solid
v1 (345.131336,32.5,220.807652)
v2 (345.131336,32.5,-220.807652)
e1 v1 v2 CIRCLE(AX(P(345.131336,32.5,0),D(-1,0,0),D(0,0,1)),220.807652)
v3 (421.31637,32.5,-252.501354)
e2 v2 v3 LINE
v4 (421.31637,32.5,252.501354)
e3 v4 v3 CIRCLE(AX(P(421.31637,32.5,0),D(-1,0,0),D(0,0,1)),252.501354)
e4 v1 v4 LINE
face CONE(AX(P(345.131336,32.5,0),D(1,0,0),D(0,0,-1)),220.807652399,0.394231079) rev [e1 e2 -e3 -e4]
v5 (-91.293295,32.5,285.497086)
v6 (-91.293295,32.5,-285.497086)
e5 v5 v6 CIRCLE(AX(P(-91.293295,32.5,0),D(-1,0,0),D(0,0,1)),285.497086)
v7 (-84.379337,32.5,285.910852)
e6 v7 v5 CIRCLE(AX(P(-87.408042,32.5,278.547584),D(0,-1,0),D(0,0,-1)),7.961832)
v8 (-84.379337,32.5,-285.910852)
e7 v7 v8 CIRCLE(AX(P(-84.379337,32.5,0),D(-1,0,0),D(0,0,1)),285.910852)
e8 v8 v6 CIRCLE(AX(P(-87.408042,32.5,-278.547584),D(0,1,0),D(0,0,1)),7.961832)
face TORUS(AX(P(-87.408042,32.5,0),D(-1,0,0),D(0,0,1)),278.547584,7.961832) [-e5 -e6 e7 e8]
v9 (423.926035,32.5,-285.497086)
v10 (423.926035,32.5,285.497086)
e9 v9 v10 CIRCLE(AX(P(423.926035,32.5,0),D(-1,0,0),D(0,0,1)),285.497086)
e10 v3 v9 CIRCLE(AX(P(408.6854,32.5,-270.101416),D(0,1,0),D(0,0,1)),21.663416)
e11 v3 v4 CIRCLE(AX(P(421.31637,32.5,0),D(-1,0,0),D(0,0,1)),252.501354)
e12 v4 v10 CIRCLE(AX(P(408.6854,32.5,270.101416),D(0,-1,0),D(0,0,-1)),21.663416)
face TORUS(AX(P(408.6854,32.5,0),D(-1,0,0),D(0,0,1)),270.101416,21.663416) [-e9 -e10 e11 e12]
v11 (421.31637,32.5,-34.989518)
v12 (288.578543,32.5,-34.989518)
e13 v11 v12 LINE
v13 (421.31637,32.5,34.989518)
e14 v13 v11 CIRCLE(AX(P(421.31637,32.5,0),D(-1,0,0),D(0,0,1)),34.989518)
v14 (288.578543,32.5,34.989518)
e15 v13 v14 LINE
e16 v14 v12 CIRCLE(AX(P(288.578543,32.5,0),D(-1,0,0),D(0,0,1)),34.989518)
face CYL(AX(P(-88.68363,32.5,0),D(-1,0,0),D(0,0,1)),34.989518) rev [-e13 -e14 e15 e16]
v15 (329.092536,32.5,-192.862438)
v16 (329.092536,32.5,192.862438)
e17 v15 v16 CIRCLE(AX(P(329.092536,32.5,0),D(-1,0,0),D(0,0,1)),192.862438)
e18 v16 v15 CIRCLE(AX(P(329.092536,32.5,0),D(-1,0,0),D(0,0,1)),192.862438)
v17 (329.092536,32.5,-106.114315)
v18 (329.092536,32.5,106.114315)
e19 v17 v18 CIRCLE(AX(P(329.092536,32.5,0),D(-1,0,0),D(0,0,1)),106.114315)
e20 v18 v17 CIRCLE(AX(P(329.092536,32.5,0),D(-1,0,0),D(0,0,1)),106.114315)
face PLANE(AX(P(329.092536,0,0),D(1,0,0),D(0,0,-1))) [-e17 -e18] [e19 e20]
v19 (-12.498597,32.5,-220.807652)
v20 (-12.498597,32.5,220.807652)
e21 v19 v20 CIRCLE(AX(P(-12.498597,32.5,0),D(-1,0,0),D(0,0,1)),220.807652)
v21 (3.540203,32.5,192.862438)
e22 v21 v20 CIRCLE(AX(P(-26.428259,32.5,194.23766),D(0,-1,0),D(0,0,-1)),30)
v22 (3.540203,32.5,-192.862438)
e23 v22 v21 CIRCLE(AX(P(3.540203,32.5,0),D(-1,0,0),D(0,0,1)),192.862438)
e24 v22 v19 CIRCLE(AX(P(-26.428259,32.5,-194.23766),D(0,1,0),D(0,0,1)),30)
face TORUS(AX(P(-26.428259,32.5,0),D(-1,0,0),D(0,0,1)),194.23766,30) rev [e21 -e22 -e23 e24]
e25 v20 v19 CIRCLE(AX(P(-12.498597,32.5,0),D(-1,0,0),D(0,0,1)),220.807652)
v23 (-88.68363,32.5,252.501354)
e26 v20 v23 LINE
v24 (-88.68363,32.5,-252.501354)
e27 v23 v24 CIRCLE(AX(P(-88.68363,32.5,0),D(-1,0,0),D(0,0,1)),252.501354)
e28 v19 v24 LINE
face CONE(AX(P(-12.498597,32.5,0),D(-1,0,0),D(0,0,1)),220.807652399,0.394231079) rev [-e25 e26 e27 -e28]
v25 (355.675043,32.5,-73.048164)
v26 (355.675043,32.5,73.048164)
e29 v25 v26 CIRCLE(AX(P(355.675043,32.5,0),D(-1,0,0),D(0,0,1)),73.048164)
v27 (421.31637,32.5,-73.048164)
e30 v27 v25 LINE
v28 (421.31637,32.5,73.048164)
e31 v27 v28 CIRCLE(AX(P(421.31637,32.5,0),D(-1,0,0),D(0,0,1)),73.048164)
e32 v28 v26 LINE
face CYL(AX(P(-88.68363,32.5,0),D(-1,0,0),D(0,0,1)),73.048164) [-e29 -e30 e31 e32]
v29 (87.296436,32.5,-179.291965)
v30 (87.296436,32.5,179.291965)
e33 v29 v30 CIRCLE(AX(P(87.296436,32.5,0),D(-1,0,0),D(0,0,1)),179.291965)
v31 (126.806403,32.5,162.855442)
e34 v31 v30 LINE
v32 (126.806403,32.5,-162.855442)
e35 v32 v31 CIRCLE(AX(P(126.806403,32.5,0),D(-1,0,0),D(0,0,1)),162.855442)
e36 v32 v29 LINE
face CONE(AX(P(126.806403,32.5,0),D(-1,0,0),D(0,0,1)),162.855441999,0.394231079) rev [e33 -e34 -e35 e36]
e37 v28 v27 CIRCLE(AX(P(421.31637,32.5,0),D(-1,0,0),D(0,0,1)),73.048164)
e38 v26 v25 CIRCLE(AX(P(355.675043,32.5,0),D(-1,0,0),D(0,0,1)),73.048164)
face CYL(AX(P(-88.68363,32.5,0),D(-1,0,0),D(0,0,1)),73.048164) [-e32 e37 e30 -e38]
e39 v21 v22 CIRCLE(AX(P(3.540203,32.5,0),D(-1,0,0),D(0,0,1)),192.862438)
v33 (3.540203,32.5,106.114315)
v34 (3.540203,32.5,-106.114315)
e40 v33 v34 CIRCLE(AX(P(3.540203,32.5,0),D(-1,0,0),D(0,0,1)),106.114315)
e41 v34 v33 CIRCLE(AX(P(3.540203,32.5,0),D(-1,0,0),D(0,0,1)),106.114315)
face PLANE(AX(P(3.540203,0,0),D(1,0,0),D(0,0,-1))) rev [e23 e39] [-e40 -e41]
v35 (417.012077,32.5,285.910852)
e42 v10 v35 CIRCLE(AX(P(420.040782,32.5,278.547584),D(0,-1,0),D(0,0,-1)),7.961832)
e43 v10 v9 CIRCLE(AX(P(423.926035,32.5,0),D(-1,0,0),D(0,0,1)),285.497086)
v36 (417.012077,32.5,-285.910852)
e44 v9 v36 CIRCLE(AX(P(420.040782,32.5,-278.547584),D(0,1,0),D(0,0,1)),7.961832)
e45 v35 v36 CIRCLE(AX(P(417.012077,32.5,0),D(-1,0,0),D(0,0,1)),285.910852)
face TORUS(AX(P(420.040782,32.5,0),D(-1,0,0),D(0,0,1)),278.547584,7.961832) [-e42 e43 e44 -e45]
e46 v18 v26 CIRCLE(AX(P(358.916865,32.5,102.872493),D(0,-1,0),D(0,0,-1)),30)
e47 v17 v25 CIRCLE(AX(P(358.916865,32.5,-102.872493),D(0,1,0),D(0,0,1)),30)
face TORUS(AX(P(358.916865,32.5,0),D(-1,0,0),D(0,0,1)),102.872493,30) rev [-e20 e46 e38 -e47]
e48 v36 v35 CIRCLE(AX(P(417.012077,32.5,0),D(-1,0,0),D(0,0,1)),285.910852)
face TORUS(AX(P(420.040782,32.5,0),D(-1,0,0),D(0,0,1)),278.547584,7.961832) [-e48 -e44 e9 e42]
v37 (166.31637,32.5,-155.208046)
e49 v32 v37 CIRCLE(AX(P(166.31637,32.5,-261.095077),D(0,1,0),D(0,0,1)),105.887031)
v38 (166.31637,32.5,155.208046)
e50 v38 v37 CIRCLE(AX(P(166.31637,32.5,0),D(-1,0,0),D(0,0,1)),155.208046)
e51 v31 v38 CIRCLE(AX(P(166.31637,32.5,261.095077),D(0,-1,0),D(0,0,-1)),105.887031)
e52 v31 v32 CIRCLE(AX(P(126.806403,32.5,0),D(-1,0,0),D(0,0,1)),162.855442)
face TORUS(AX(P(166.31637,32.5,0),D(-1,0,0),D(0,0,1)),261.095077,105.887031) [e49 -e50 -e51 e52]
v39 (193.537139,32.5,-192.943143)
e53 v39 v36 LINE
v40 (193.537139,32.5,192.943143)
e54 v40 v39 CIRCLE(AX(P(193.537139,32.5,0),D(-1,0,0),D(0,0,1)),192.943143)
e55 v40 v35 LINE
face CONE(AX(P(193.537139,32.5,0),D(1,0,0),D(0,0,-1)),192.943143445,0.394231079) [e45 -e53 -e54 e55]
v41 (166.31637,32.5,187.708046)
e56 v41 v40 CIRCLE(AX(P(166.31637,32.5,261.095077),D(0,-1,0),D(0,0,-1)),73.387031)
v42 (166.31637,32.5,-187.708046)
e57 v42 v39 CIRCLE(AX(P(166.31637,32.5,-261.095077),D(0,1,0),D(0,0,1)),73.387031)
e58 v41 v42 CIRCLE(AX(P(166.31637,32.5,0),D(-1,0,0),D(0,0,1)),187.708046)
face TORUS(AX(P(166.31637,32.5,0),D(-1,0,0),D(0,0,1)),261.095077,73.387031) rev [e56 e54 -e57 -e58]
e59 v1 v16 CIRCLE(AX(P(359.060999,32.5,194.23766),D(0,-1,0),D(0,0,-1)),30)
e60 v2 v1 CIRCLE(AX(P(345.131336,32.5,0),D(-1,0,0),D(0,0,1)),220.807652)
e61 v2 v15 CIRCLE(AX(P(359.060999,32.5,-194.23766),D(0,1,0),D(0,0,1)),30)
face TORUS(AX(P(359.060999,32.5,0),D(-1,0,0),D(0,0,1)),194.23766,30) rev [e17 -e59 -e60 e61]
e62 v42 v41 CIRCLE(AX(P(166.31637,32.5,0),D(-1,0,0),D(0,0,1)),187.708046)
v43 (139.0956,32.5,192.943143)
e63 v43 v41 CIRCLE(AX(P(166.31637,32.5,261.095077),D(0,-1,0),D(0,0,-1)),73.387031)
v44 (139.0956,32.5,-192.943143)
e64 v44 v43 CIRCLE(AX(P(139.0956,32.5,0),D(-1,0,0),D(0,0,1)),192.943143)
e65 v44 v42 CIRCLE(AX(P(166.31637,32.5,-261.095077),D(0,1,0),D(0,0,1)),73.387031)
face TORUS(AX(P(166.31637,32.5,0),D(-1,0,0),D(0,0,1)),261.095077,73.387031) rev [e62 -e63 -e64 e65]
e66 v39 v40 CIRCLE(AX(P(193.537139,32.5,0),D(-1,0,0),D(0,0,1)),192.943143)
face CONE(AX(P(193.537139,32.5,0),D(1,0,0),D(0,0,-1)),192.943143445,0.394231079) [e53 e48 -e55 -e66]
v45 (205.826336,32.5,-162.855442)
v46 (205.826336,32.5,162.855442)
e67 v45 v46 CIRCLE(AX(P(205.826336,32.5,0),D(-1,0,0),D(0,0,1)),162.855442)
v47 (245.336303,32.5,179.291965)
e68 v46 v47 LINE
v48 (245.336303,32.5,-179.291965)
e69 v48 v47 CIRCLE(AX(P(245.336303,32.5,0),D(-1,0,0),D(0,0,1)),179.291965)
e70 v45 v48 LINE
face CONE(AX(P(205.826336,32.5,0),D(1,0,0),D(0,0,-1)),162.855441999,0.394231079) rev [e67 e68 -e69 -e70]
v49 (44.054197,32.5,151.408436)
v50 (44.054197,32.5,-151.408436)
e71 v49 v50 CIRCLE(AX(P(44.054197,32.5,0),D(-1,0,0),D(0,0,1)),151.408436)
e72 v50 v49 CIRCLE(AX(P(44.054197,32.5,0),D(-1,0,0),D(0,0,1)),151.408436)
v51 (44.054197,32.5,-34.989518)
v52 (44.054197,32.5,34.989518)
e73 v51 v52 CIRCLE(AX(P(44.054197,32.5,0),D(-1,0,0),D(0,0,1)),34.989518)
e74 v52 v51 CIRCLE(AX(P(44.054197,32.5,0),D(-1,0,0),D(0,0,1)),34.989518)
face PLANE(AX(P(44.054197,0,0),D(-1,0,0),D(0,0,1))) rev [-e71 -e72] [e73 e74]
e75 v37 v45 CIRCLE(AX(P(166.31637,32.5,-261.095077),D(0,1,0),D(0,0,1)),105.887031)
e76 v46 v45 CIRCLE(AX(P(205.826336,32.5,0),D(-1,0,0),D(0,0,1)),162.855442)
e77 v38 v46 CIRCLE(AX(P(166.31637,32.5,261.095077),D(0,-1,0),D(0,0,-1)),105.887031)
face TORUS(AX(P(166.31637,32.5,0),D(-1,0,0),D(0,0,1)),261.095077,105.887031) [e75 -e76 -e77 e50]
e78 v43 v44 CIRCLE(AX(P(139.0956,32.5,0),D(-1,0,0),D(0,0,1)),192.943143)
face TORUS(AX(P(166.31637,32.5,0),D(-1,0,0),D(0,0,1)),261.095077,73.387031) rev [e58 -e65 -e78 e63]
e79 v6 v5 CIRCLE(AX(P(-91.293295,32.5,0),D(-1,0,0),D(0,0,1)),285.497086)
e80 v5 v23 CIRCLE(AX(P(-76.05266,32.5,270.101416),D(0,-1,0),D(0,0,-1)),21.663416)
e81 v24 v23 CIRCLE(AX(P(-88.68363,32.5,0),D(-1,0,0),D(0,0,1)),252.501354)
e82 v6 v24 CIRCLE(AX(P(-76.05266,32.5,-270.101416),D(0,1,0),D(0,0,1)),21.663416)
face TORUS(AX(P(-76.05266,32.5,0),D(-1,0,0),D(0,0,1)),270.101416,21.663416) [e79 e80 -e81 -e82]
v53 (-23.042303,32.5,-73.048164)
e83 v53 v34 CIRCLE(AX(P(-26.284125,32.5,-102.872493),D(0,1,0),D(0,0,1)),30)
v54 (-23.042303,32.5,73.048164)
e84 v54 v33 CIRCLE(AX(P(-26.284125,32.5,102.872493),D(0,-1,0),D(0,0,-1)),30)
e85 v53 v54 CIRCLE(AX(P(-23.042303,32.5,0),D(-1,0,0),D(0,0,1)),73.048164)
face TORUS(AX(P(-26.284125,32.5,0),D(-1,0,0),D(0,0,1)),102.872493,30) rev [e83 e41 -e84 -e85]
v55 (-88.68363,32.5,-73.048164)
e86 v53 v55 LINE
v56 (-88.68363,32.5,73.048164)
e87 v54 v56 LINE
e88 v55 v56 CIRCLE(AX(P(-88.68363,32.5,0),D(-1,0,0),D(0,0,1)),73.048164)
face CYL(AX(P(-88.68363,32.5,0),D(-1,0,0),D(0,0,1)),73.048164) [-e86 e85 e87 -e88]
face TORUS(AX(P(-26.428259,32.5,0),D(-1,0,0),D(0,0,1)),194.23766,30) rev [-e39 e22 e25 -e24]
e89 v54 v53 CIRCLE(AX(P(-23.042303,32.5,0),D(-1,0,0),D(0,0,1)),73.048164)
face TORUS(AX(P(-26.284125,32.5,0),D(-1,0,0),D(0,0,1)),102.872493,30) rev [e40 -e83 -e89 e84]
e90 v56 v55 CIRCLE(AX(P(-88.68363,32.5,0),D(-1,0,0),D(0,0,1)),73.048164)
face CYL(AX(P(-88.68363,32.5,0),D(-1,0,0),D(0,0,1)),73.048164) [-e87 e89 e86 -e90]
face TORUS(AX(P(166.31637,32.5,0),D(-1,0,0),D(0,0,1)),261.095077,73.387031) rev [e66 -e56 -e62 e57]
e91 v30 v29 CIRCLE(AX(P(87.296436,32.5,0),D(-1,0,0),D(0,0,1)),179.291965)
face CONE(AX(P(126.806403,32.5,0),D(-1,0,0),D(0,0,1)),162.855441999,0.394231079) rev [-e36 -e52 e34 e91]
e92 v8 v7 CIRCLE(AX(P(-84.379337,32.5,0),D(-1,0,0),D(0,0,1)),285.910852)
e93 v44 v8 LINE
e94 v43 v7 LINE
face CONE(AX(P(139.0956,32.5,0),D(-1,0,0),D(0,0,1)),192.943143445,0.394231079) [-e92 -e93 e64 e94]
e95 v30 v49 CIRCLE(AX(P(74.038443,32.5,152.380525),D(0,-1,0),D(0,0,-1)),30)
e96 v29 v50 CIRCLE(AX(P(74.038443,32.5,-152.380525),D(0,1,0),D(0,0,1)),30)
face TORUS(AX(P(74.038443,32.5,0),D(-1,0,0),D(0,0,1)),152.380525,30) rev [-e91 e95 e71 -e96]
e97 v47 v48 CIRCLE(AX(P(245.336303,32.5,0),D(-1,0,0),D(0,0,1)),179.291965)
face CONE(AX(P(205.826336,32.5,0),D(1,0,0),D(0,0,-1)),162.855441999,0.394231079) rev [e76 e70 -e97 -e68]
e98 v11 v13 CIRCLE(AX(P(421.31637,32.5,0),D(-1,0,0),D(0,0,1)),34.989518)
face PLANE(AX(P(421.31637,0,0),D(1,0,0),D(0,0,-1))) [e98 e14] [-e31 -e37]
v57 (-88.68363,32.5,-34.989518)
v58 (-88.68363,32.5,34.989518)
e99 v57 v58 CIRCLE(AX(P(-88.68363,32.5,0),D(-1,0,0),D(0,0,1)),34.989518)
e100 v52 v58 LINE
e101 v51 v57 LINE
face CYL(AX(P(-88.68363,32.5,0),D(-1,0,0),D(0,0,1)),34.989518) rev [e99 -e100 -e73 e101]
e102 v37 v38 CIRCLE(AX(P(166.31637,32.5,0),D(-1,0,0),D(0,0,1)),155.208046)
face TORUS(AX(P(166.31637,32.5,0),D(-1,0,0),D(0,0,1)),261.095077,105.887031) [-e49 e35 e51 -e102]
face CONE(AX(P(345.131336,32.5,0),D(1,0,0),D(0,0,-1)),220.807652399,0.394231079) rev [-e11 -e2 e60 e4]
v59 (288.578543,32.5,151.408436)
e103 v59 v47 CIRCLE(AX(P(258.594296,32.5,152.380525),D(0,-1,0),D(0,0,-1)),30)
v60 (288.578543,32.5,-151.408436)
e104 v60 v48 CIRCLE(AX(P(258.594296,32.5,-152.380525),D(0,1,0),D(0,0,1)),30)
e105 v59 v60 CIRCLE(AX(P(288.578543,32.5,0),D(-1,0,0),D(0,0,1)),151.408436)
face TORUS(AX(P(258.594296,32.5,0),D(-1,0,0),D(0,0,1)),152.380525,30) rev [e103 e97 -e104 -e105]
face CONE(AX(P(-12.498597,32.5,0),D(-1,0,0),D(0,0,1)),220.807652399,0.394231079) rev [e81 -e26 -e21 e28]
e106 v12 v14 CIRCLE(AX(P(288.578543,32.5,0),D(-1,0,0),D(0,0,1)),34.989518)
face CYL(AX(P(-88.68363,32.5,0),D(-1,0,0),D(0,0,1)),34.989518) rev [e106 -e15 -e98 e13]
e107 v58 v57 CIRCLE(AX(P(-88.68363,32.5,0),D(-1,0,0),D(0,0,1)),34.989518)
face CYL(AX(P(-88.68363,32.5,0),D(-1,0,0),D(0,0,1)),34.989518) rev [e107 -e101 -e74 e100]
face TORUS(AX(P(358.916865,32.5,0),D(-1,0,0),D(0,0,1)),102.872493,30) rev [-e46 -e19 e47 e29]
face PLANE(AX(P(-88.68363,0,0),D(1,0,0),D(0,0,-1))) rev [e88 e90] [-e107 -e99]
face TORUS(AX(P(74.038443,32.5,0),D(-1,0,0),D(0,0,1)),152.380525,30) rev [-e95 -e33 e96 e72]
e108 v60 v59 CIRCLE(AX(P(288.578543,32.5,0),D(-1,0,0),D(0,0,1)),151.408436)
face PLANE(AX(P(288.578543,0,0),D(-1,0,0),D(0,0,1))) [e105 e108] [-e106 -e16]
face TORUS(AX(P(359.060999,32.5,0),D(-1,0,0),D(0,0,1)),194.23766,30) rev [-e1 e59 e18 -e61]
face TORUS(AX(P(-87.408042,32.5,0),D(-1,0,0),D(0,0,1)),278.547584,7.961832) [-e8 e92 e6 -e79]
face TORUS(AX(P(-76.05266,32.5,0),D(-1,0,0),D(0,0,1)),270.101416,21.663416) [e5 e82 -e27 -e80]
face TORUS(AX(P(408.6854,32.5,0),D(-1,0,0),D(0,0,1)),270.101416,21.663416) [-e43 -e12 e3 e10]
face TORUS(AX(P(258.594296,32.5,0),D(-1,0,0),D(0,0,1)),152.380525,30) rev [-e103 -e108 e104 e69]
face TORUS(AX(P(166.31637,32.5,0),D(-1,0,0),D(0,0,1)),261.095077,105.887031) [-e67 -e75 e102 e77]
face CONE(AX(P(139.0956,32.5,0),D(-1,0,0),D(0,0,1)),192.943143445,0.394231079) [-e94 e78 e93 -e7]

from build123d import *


with BuildPart() as part:
    # Cap Profile Sketch → Cap Body Revolve 360 (revolve)
    with BuildSketch(Plane.XY, mode=Mode.PRIVATE) as cap_body_revolve_360_sk:
        with BuildLine():
            Line((288.578542668, 183.908436408), (288.578542668, 67.489517857))
            Line((288.578542668, 67.489517857), (421.316369772, 67.489517857))
            Line((421.316369772, 67.489517857), (421.316369772, 105.548164289))
            Line((421.316369772, 105.548164289), (355.675042918, 105.548164289))
            ThreePointArc((355.675042918, 105.548164289), (335.535565441, 116.575822282), (329.092536094, 138.614315123))
            Line((329.092536094, 138.614315123), (329.092536094, 225.362437801))
            ThreePointArc((329.092536094, 225.362437801), (329.060998923, 226.737659861), (329.092536094, 228.112881921))
            ThreePointArc((329.092536094, 228.112881921), (333.753777304, 242.848045765), (345.131336453, 253.307652399))
            Line((345.131336453, 253.307652399), (421.316369772, 285.001353838))
            ThreePointArc((421.316369772, 285.001353838), (430.28137568, 300.893369363), (423.926034603, 317.997086158))
            ThreePointArc((423.926034603, 317.997086158), (420.516406834, 318.995196726), (417.01207704, 318.410851852))
            Line((417.01207704, 318.410851852), (236.369669575, 243.261885185))
            Line((236.369669575, 243.261885185), (193.537139087, 225.443143445))
            ThreePointArc((193.537139087, 225.443143445), (166.316369772, 220.208045956), (139.095600457, 225.443143445))
            Line((139.095600457, 225.443143445), (-84.379337496, 318.410851852))
            ThreePointArc((-84.379337496, 318.410851852), (-87.88366729, 318.995196726), (-91.29329506, 317.997086158))
            ThreePointArc((-91.29329506, 317.997086158), (-97.648636136, 300.893369363), (-88.683630228, 285.001353838))
            Line((-88.683630228, 285.001353838), (-12.498596909, 253.307652399))
            ThreePointArc((-12.498596909, 253.307652399), (-1.12103776, 242.848045765), (3.54020345, 228.112881921))
            ThreePointArc((3.54020345, 228.112881921), (3.571740621, 226.737659861), (3.54020345, 225.362437801))
            Line((3.54020345, 225.362437801), (3.54020345, 138.614315123))
            ThreePointArc((3.54020345, 138.614315123), (-2.902825897, 116.575822282), (-23.042303374, 105.548164289))
            Line((-23.042303374, 105.548164289), (-88.683630228, 105.548164289))
            Line((-88.683630228, 105.548164289), (-88.683630228, 67.489517857))
            Line((-88.683630228, 67.489517857), (44.054196876, 67.489517857))
            Line((44.054196876, 67.489517857), (44.054196876, 183.908436408))
            ThreePointArc((44.054196876, 183.908436408), (56.212998599, 209.010454978), (83.779873144, 213.254889383))
            ThreePointArc((83.779873144, 213.254889383), (85.561394381, 212.579290467), (87.296436491, 211.791965448))
            Line((87.296436491, 211.791965448), (126.806403131, 195.355441999))
            ThreePointArc((126.806403131, 195.355441999), (166.316369772, 187.708045956), (205.826336413, 195.355441999))
            Line((205.826336413, 195.355441999), (245.336303053, 211.791965448))
            ThreePointArc((245.336303053, 211.791965448), (247.071345163, 212.579290467), (248.8528664, 213.254889383))
            ThreePointArc((248.8528664, 213.254889383), (276.419740944, 209.010454978), (288.578542668, 183.908436408))
        make_face()
    revolve(cap_body_revolve_360_sk.sketch.rotate(Axis((-88.683630228, 32.5, 0), (1, 0, 0)), 90), axis=Axis((-88.683630228, 32.5, 0), (1, 0, 0)))


solid = part.part
